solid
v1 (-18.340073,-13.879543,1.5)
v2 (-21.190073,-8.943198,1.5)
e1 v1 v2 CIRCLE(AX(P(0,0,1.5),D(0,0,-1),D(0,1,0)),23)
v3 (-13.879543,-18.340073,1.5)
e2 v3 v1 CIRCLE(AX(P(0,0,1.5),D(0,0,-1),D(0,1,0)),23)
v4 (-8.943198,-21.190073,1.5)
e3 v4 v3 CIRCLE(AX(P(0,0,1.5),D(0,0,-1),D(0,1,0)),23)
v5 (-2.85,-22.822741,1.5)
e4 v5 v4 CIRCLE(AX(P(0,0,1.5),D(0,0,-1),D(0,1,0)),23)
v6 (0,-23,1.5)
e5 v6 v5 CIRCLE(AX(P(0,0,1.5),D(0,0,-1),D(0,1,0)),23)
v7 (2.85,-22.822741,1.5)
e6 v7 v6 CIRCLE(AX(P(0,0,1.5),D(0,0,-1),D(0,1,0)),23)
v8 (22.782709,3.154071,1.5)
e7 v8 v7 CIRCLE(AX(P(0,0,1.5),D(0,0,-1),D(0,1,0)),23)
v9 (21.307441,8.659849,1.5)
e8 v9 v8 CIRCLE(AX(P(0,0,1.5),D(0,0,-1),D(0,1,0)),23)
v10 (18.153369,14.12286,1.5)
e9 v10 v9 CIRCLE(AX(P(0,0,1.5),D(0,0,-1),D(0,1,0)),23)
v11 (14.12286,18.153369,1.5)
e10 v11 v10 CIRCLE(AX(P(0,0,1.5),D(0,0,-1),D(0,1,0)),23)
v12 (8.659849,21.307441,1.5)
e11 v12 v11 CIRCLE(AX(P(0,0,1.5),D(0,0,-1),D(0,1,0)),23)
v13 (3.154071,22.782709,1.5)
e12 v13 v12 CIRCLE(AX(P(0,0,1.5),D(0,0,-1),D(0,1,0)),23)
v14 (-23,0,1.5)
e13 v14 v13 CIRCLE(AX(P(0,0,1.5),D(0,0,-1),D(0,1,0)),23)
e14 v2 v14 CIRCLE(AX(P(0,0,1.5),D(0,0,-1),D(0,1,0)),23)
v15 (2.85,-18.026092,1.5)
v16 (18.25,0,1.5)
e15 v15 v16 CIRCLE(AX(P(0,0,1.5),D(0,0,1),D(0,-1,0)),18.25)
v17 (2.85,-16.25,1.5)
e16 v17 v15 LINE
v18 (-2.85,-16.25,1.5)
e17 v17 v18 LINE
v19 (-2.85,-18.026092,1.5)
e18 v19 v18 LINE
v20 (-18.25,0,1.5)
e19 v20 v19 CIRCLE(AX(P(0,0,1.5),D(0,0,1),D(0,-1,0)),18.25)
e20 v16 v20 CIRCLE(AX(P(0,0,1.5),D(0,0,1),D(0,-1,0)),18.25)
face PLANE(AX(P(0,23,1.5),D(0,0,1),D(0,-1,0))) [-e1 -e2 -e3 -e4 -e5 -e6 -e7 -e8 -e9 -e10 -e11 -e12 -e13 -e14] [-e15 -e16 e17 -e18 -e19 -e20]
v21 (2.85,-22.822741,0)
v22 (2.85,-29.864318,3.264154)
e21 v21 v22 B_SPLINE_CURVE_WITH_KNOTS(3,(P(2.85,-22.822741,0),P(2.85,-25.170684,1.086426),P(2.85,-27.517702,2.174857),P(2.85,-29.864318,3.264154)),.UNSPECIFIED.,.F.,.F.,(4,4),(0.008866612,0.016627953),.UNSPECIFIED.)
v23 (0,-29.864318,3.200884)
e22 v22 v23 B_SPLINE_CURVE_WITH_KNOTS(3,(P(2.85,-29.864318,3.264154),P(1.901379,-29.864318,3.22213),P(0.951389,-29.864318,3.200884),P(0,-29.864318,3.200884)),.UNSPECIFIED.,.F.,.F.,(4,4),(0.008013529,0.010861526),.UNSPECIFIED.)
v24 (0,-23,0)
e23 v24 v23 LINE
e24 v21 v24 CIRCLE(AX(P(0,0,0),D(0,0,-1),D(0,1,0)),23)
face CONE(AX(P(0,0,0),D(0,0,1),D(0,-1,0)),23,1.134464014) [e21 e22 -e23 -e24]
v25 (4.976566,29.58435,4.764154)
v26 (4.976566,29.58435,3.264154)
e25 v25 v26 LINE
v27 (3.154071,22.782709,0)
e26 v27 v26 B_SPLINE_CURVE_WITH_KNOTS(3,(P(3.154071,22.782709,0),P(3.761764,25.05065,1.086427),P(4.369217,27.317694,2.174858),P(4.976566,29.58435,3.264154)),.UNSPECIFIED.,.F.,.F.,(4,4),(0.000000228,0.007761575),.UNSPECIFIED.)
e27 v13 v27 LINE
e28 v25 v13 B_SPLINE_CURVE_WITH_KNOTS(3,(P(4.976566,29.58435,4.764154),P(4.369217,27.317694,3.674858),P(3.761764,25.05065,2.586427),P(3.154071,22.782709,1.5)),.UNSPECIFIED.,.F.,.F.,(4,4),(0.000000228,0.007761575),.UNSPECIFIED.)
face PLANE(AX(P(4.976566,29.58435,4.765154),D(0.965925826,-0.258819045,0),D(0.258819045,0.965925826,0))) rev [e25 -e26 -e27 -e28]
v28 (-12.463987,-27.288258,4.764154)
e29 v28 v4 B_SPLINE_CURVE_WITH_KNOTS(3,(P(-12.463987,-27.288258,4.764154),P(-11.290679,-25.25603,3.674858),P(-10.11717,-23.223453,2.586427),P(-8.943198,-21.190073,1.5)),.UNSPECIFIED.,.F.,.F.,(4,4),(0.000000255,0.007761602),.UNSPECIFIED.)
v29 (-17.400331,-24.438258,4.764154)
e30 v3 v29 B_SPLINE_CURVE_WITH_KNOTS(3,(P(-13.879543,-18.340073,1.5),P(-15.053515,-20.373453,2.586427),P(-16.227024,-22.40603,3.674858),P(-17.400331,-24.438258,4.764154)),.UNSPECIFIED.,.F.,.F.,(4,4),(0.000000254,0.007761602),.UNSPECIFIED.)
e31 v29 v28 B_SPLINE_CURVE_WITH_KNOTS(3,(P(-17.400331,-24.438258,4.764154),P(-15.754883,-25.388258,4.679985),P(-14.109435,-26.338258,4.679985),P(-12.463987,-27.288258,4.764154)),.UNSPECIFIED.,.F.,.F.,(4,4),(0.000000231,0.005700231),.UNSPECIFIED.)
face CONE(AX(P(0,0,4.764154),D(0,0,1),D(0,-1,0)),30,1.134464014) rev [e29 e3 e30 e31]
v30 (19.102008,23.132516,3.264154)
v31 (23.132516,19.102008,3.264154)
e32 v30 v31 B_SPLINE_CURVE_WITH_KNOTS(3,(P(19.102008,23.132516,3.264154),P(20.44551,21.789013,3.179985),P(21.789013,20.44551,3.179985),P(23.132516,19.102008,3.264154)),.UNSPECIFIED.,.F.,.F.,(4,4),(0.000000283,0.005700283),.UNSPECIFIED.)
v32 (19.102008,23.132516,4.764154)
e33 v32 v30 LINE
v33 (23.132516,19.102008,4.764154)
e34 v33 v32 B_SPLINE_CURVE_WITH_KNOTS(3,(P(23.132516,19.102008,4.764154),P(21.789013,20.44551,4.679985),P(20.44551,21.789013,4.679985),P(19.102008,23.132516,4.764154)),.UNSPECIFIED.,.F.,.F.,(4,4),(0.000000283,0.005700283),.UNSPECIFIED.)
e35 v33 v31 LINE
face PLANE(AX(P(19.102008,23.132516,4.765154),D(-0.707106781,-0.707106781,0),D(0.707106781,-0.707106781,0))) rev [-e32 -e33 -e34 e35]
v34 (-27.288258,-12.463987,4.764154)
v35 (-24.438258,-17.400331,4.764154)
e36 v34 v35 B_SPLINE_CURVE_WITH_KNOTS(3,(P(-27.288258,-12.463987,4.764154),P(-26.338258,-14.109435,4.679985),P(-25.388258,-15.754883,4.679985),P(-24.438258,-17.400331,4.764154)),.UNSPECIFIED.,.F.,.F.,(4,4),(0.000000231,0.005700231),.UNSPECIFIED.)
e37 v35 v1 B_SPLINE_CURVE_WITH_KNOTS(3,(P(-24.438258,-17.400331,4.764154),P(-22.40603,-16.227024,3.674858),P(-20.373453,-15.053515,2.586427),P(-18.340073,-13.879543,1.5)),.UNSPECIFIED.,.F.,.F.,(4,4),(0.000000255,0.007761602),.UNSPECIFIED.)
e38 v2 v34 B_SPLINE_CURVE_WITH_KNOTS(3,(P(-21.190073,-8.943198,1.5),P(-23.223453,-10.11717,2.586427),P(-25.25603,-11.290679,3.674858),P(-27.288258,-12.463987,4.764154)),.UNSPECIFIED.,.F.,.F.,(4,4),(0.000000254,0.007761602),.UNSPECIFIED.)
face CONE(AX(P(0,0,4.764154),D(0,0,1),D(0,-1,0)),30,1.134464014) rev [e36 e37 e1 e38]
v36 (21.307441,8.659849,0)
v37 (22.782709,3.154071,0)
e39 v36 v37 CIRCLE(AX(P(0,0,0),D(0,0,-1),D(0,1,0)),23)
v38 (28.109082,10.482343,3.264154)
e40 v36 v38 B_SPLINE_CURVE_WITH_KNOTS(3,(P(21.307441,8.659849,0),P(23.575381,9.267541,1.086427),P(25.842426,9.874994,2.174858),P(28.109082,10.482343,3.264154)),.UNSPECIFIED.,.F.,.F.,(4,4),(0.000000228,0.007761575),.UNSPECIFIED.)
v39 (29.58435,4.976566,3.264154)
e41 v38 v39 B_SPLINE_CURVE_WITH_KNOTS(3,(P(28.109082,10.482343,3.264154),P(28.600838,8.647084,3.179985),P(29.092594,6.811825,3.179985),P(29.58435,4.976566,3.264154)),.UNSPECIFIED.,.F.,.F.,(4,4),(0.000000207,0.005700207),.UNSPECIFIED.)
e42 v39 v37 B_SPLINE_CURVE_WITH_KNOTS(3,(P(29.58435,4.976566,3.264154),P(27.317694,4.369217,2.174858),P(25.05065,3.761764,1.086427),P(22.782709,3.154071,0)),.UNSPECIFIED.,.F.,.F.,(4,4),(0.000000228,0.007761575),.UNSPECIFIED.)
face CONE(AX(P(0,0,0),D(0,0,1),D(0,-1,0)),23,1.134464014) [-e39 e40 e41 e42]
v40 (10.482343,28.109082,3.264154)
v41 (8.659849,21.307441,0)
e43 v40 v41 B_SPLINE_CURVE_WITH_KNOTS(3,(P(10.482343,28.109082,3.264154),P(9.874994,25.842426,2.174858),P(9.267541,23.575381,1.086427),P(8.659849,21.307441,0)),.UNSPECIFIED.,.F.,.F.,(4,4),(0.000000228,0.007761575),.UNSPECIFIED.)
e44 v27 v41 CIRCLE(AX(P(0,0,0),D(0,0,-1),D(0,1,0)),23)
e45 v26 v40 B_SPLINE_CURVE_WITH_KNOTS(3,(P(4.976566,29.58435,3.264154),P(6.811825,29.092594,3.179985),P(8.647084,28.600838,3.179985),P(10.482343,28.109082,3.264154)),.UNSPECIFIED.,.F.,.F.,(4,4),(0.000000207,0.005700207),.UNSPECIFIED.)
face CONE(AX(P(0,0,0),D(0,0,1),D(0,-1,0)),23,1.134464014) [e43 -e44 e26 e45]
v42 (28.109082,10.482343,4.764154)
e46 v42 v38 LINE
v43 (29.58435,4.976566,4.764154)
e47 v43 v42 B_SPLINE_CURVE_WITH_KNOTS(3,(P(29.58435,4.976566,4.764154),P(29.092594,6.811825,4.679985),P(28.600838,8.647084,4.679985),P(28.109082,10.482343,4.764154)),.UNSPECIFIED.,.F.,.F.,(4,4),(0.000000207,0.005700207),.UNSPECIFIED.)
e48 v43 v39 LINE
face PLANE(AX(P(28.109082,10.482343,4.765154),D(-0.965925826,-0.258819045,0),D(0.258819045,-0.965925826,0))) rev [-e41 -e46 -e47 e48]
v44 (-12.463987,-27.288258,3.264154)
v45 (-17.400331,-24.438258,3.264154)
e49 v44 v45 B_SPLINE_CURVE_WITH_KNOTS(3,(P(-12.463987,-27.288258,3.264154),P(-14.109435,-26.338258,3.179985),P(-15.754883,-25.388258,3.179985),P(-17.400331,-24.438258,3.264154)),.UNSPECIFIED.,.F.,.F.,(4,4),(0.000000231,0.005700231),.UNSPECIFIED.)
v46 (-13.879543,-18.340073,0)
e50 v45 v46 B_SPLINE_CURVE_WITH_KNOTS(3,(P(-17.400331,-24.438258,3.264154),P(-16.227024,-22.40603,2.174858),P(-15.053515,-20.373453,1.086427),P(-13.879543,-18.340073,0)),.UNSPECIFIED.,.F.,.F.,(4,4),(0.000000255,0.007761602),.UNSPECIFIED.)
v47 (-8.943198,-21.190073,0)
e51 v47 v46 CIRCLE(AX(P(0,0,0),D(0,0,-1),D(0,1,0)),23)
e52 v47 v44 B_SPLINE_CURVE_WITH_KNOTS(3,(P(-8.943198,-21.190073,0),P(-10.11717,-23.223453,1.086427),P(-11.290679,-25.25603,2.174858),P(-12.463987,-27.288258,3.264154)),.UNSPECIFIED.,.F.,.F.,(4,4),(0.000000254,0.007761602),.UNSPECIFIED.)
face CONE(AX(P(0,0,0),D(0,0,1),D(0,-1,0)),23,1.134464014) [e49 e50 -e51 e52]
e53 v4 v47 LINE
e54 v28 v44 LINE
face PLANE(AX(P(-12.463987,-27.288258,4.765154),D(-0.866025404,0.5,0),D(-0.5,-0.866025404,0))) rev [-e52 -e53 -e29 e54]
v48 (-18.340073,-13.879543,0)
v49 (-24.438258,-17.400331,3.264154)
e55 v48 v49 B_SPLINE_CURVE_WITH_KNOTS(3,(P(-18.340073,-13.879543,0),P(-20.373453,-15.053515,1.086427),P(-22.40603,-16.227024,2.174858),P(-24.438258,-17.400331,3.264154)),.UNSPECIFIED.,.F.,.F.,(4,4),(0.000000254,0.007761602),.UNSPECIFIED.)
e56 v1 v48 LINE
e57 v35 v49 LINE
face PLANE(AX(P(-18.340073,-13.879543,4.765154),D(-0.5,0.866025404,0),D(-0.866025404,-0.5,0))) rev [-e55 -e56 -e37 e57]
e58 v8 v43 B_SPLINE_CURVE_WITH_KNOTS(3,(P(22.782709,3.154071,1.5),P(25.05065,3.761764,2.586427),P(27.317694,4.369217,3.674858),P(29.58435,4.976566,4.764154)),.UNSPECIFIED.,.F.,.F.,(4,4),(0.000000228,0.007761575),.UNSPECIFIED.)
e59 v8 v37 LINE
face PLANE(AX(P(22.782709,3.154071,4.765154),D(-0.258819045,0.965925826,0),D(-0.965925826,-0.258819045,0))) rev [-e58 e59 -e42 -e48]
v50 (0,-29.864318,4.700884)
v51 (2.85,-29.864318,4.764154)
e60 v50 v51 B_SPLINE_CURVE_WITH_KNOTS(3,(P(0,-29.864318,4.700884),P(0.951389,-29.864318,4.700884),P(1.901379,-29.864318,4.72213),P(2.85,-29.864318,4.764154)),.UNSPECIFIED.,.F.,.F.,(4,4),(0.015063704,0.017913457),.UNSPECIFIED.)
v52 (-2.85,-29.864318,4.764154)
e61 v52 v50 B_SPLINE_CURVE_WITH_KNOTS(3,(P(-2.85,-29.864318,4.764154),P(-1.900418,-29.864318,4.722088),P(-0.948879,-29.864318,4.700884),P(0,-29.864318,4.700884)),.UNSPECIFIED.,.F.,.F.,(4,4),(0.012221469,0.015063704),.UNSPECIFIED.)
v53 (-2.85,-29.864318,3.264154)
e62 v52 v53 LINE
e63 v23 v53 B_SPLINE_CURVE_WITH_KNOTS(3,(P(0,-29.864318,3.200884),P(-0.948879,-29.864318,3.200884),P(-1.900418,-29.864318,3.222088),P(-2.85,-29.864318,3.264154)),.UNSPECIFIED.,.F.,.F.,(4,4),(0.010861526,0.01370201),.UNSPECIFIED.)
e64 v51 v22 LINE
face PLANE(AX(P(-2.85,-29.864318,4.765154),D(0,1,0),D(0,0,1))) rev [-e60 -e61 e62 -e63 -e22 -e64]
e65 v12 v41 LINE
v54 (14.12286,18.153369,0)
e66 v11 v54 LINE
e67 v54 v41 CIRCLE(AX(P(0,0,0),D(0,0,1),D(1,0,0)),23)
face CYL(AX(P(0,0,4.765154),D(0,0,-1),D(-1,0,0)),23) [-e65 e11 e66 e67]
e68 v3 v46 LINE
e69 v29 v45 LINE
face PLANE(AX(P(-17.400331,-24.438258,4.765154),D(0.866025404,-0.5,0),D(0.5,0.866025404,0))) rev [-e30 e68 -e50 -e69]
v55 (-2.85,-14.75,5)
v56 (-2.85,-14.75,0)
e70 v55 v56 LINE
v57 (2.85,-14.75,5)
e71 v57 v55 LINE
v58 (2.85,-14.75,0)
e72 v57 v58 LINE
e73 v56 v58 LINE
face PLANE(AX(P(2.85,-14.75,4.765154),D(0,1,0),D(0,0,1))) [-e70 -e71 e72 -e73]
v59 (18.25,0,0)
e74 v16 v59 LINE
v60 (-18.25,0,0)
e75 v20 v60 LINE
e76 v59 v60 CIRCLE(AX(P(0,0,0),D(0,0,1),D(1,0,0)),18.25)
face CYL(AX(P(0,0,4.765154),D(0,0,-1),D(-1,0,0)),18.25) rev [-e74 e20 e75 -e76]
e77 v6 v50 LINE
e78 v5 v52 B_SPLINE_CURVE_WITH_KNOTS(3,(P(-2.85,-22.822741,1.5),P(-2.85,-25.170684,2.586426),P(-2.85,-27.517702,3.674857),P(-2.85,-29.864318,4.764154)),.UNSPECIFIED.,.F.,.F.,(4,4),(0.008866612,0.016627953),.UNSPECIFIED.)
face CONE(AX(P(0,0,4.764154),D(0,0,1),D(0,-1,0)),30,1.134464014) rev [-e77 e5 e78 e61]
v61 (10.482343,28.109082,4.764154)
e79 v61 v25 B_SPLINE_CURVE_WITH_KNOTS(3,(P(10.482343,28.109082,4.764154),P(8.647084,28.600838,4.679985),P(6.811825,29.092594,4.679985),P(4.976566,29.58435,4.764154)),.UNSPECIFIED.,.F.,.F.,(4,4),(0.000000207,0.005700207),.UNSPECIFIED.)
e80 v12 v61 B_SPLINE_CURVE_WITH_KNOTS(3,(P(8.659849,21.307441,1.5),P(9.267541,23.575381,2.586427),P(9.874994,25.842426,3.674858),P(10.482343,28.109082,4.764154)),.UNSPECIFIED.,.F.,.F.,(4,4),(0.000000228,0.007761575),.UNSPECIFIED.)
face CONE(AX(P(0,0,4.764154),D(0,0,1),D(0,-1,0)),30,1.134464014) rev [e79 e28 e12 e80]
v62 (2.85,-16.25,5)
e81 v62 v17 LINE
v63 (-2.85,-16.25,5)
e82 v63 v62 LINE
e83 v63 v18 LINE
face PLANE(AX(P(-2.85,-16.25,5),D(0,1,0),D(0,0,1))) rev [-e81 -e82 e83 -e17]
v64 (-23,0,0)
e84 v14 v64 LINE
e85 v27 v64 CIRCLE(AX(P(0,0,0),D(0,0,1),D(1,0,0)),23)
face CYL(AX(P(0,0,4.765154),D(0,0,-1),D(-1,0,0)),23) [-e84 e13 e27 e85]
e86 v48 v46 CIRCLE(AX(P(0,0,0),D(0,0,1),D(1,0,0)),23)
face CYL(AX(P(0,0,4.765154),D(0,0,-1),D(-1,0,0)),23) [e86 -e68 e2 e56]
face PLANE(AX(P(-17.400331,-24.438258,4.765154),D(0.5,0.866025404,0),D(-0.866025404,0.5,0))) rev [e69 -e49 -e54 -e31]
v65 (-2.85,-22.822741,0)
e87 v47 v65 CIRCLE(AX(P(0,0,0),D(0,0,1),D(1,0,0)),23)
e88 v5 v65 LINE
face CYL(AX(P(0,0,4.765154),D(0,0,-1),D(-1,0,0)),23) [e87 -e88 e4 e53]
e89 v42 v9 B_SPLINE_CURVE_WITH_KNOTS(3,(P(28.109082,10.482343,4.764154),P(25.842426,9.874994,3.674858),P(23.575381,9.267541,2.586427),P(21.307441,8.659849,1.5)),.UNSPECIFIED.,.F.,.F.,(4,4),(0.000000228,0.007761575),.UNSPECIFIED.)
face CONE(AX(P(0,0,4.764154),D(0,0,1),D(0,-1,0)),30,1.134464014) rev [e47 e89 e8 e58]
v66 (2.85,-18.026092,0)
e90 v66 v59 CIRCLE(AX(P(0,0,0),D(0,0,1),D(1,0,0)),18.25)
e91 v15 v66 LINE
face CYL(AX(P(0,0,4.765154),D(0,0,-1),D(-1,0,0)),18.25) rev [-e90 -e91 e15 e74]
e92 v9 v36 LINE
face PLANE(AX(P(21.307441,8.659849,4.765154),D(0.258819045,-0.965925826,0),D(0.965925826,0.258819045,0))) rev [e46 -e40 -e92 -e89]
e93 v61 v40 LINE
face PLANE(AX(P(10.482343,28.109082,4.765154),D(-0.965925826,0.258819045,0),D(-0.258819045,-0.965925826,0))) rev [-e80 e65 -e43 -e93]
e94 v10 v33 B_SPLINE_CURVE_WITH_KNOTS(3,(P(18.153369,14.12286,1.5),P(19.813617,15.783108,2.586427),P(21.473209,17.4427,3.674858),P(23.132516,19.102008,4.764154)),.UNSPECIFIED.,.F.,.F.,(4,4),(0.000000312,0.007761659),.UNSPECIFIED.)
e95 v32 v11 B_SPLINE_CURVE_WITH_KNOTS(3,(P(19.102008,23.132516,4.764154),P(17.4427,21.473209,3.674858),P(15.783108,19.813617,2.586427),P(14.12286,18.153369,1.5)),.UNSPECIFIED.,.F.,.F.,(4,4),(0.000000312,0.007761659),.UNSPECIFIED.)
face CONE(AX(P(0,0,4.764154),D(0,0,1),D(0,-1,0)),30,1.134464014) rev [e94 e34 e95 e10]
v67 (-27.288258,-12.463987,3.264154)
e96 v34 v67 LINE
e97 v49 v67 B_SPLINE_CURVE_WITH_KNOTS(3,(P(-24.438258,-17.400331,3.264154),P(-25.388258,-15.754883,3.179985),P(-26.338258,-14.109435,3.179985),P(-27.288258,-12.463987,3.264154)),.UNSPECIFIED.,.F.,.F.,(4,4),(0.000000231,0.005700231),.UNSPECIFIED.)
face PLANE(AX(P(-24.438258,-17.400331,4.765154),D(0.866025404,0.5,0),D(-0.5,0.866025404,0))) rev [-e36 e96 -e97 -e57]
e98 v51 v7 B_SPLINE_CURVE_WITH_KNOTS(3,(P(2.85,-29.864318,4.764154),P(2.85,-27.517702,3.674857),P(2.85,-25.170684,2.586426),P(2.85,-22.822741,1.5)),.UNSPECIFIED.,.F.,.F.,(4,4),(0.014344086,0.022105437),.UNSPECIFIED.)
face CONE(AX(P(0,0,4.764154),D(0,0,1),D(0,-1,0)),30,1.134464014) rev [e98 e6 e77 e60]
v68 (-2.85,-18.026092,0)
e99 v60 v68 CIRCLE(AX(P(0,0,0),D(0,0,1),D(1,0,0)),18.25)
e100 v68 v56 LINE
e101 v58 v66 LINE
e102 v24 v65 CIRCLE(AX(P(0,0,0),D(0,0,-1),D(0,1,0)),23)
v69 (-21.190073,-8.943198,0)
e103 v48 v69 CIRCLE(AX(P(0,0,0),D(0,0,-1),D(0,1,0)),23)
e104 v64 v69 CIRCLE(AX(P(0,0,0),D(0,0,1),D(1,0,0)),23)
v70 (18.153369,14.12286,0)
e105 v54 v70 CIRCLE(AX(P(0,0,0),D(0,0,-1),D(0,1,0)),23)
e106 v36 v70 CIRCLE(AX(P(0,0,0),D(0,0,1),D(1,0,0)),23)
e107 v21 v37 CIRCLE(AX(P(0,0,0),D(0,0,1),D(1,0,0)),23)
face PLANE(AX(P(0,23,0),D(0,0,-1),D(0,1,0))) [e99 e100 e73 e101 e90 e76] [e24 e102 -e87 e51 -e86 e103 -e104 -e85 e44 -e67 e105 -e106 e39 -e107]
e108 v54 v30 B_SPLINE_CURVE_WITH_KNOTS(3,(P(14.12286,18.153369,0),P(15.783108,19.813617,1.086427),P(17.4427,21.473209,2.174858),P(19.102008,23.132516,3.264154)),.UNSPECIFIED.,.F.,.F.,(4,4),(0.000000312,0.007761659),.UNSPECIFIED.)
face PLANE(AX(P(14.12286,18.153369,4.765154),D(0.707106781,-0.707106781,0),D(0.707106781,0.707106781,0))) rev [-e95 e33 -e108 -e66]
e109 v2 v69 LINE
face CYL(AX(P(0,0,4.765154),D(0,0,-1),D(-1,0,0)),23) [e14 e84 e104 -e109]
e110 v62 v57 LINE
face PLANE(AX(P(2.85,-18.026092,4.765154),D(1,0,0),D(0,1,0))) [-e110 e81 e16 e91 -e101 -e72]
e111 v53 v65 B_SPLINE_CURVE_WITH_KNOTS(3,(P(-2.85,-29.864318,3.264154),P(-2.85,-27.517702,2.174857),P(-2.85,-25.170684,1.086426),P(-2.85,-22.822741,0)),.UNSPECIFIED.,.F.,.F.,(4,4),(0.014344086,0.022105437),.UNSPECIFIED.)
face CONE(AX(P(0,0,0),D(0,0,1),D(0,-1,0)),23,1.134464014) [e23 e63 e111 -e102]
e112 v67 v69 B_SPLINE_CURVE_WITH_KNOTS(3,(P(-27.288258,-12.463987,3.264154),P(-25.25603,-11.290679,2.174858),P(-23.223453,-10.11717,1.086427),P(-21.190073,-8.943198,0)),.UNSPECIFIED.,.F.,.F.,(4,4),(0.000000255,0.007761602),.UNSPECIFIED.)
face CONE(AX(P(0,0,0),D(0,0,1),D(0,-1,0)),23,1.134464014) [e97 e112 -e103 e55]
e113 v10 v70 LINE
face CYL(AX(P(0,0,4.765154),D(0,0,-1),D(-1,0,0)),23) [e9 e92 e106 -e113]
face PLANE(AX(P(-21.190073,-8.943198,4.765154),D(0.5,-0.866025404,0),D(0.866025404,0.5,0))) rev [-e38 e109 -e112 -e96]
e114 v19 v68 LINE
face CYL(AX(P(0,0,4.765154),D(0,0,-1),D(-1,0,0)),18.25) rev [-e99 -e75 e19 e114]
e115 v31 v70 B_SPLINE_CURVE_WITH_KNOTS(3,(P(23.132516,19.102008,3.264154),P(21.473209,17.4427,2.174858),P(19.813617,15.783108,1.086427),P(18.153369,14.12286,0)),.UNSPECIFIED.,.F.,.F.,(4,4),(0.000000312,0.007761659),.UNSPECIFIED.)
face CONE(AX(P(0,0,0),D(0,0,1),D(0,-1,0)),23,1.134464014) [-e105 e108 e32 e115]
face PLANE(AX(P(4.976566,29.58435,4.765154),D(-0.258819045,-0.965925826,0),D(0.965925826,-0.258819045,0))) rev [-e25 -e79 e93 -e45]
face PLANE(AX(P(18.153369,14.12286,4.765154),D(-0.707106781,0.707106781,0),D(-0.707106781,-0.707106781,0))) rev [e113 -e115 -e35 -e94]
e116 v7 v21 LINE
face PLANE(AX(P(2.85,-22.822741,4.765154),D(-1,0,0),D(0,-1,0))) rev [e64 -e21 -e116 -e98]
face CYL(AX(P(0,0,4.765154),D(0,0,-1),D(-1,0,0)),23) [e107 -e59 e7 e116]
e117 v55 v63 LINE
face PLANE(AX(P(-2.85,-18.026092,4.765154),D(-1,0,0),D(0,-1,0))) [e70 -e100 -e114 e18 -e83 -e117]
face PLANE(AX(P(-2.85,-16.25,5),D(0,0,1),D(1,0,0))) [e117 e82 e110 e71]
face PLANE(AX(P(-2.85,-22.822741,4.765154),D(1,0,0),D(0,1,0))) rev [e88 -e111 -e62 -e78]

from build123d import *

# Parameters (mm, degrees)
CUT_EXTRUDE_START   = -2e-06
SKETCH_3_OUTSIDE_W  = 78.998
SKETCH_3_OUTSIDE_H  = 78.998
CUT_EXTRUDE_2_DEPTH = 4.764157
SKETCH_4_W          = 5.7
SKETCH_4_H          = 1.5
EXTRUDE_1_DEPTH     = 5


with BuildPart() as part:
    # 草图2 → Revolve 544 (revolve)
    with BuildSketch(Plane(origin=(0, 0, 0), x_dir=(0, 0, -1), z_dir=(1, 0, 0))):
        Polygon((-3.264153607, 30), (0, 23), (0, 0), (-1.5, 0), (-1.5, 23), (-4.764153607, 30), align=None)
    revolve(axis=Axis((0, 0, 0), (0, 0, 1)))

    # 草图3 outside → 切除-拉伸2 (cut)
    # profile 1 of 2: a face of its own
    with BuildSketch(Plane.XY.offset(CUT_EXTRUDE_START)):
        Rectangle(SKETCH_3_OUTSIDE_W, SKETCH_3_OUTSIDE_H)
        with BuildLine():
            Line((-2.85, -22.822740852), (-2.85, -29.864318174))
            Line((-2.85, -29.864318174), (2.85, -29.864318174))
            Line((2.85, -29.864318174), (2.85, -22.822740852))
            ThreePointArc((2.85, -22.822740852), (18.247126827, -14.001512867), (22.782709094, 3.154071389))
            Line((22.782709094, 3.154071389), (29.584350487, 4.976565708))
            Line((29.584350487, 4.976565708), (28.10908193, 10.482342917))
            Line((28.10908193, 10.482342917), (21.307440537, 8.659848599))
            ThreePointArc((21.307440537, 8.659848599), (19.918584287, 11.5), (18.153369148, 14.122860495))
            Line((18.153369148, 14.122860495), (23.132516223, 19.10200757))
            Line((23.132516223, 19.10200757), (19.10200757, 23.132516223))
            Line((19.10200757, 23.132516223), (14.122860495, 18.153369148))
            ThreePointArc((14.122860495, 18.153369148), (11.5, 19.918584287), (8.659848599, 21.307440537))
            Line((8.659848599, 21.307440537), (10.482342917, 28.10908193))
            Line((10.482342917, 28.10908193), (4.976565708, 29.584350487))
            Line((4.976565708, 29.584350487), (3.154071389, 22.782709094))
            ThreePointArc((3.154071389, 22.782709094), (-18.247126827, 14.001512867), (-21.190073362, -8.943198025))
            Line((-21.190073362, -8.943198025), (-27.288258205, -12.463986686))
            Line((-27.288258205, -12.463986686), (-24.438258205, -17.400331488))
            Line((-24.438258205, -17.400331488), (-18.340073362, -13.879542827))
            ThreePointArc((-18.340073362, -13.879542827), (-16.263455967, -16.263455967), (-13.879542827, -18.340073362))
            Line((-13.879542827, -18.340073362), (-17.400331488, -24.438258205))
            Line((-17.400331488, -24.438258205), (-12.463986686, -27.288258205))
            Line((-12.463986686, -27.288258205), (-8.943198025, -21.190073362))
            ThreePointArc((-8.943198025, -21.190073362), (-5.952838037, -22.216294005), (-2.85, -22.822740852))
        make_face(mode=Mode.SUBTRACT)
    # profile 2 of 2: a face of its own
    with BuildSketch(Plane.XY.offset(CUT_EXTRUDE_START)):
        with BuildLine():
            Line((2.85, -18.0260922), (2.85, -14.75))
            Line((2.85, -14.75), (-2.85, -14.75))
            Line((-2.85, -14.75), (-2.85, -18.0260922))
            ThreePointArc((-2.85, -18.0260922), (0, 18.25), (2.85, -18.0260922))
        make_face()
    extrude(amount=CUT_EXTRUDE_2_DEPTH, mode=Mode.SUBTRACT)

    # 草图4 → 凸台-拉伸1 (add)
    with BuildSketch(Plane.XY):
        with Locations((0, -15.5)):
            Rectangle(SKETCH_4_W, SKETCH_4_H)
    extrude(amount=EXTRUDE_1_DEPTH)


solid = part.part
